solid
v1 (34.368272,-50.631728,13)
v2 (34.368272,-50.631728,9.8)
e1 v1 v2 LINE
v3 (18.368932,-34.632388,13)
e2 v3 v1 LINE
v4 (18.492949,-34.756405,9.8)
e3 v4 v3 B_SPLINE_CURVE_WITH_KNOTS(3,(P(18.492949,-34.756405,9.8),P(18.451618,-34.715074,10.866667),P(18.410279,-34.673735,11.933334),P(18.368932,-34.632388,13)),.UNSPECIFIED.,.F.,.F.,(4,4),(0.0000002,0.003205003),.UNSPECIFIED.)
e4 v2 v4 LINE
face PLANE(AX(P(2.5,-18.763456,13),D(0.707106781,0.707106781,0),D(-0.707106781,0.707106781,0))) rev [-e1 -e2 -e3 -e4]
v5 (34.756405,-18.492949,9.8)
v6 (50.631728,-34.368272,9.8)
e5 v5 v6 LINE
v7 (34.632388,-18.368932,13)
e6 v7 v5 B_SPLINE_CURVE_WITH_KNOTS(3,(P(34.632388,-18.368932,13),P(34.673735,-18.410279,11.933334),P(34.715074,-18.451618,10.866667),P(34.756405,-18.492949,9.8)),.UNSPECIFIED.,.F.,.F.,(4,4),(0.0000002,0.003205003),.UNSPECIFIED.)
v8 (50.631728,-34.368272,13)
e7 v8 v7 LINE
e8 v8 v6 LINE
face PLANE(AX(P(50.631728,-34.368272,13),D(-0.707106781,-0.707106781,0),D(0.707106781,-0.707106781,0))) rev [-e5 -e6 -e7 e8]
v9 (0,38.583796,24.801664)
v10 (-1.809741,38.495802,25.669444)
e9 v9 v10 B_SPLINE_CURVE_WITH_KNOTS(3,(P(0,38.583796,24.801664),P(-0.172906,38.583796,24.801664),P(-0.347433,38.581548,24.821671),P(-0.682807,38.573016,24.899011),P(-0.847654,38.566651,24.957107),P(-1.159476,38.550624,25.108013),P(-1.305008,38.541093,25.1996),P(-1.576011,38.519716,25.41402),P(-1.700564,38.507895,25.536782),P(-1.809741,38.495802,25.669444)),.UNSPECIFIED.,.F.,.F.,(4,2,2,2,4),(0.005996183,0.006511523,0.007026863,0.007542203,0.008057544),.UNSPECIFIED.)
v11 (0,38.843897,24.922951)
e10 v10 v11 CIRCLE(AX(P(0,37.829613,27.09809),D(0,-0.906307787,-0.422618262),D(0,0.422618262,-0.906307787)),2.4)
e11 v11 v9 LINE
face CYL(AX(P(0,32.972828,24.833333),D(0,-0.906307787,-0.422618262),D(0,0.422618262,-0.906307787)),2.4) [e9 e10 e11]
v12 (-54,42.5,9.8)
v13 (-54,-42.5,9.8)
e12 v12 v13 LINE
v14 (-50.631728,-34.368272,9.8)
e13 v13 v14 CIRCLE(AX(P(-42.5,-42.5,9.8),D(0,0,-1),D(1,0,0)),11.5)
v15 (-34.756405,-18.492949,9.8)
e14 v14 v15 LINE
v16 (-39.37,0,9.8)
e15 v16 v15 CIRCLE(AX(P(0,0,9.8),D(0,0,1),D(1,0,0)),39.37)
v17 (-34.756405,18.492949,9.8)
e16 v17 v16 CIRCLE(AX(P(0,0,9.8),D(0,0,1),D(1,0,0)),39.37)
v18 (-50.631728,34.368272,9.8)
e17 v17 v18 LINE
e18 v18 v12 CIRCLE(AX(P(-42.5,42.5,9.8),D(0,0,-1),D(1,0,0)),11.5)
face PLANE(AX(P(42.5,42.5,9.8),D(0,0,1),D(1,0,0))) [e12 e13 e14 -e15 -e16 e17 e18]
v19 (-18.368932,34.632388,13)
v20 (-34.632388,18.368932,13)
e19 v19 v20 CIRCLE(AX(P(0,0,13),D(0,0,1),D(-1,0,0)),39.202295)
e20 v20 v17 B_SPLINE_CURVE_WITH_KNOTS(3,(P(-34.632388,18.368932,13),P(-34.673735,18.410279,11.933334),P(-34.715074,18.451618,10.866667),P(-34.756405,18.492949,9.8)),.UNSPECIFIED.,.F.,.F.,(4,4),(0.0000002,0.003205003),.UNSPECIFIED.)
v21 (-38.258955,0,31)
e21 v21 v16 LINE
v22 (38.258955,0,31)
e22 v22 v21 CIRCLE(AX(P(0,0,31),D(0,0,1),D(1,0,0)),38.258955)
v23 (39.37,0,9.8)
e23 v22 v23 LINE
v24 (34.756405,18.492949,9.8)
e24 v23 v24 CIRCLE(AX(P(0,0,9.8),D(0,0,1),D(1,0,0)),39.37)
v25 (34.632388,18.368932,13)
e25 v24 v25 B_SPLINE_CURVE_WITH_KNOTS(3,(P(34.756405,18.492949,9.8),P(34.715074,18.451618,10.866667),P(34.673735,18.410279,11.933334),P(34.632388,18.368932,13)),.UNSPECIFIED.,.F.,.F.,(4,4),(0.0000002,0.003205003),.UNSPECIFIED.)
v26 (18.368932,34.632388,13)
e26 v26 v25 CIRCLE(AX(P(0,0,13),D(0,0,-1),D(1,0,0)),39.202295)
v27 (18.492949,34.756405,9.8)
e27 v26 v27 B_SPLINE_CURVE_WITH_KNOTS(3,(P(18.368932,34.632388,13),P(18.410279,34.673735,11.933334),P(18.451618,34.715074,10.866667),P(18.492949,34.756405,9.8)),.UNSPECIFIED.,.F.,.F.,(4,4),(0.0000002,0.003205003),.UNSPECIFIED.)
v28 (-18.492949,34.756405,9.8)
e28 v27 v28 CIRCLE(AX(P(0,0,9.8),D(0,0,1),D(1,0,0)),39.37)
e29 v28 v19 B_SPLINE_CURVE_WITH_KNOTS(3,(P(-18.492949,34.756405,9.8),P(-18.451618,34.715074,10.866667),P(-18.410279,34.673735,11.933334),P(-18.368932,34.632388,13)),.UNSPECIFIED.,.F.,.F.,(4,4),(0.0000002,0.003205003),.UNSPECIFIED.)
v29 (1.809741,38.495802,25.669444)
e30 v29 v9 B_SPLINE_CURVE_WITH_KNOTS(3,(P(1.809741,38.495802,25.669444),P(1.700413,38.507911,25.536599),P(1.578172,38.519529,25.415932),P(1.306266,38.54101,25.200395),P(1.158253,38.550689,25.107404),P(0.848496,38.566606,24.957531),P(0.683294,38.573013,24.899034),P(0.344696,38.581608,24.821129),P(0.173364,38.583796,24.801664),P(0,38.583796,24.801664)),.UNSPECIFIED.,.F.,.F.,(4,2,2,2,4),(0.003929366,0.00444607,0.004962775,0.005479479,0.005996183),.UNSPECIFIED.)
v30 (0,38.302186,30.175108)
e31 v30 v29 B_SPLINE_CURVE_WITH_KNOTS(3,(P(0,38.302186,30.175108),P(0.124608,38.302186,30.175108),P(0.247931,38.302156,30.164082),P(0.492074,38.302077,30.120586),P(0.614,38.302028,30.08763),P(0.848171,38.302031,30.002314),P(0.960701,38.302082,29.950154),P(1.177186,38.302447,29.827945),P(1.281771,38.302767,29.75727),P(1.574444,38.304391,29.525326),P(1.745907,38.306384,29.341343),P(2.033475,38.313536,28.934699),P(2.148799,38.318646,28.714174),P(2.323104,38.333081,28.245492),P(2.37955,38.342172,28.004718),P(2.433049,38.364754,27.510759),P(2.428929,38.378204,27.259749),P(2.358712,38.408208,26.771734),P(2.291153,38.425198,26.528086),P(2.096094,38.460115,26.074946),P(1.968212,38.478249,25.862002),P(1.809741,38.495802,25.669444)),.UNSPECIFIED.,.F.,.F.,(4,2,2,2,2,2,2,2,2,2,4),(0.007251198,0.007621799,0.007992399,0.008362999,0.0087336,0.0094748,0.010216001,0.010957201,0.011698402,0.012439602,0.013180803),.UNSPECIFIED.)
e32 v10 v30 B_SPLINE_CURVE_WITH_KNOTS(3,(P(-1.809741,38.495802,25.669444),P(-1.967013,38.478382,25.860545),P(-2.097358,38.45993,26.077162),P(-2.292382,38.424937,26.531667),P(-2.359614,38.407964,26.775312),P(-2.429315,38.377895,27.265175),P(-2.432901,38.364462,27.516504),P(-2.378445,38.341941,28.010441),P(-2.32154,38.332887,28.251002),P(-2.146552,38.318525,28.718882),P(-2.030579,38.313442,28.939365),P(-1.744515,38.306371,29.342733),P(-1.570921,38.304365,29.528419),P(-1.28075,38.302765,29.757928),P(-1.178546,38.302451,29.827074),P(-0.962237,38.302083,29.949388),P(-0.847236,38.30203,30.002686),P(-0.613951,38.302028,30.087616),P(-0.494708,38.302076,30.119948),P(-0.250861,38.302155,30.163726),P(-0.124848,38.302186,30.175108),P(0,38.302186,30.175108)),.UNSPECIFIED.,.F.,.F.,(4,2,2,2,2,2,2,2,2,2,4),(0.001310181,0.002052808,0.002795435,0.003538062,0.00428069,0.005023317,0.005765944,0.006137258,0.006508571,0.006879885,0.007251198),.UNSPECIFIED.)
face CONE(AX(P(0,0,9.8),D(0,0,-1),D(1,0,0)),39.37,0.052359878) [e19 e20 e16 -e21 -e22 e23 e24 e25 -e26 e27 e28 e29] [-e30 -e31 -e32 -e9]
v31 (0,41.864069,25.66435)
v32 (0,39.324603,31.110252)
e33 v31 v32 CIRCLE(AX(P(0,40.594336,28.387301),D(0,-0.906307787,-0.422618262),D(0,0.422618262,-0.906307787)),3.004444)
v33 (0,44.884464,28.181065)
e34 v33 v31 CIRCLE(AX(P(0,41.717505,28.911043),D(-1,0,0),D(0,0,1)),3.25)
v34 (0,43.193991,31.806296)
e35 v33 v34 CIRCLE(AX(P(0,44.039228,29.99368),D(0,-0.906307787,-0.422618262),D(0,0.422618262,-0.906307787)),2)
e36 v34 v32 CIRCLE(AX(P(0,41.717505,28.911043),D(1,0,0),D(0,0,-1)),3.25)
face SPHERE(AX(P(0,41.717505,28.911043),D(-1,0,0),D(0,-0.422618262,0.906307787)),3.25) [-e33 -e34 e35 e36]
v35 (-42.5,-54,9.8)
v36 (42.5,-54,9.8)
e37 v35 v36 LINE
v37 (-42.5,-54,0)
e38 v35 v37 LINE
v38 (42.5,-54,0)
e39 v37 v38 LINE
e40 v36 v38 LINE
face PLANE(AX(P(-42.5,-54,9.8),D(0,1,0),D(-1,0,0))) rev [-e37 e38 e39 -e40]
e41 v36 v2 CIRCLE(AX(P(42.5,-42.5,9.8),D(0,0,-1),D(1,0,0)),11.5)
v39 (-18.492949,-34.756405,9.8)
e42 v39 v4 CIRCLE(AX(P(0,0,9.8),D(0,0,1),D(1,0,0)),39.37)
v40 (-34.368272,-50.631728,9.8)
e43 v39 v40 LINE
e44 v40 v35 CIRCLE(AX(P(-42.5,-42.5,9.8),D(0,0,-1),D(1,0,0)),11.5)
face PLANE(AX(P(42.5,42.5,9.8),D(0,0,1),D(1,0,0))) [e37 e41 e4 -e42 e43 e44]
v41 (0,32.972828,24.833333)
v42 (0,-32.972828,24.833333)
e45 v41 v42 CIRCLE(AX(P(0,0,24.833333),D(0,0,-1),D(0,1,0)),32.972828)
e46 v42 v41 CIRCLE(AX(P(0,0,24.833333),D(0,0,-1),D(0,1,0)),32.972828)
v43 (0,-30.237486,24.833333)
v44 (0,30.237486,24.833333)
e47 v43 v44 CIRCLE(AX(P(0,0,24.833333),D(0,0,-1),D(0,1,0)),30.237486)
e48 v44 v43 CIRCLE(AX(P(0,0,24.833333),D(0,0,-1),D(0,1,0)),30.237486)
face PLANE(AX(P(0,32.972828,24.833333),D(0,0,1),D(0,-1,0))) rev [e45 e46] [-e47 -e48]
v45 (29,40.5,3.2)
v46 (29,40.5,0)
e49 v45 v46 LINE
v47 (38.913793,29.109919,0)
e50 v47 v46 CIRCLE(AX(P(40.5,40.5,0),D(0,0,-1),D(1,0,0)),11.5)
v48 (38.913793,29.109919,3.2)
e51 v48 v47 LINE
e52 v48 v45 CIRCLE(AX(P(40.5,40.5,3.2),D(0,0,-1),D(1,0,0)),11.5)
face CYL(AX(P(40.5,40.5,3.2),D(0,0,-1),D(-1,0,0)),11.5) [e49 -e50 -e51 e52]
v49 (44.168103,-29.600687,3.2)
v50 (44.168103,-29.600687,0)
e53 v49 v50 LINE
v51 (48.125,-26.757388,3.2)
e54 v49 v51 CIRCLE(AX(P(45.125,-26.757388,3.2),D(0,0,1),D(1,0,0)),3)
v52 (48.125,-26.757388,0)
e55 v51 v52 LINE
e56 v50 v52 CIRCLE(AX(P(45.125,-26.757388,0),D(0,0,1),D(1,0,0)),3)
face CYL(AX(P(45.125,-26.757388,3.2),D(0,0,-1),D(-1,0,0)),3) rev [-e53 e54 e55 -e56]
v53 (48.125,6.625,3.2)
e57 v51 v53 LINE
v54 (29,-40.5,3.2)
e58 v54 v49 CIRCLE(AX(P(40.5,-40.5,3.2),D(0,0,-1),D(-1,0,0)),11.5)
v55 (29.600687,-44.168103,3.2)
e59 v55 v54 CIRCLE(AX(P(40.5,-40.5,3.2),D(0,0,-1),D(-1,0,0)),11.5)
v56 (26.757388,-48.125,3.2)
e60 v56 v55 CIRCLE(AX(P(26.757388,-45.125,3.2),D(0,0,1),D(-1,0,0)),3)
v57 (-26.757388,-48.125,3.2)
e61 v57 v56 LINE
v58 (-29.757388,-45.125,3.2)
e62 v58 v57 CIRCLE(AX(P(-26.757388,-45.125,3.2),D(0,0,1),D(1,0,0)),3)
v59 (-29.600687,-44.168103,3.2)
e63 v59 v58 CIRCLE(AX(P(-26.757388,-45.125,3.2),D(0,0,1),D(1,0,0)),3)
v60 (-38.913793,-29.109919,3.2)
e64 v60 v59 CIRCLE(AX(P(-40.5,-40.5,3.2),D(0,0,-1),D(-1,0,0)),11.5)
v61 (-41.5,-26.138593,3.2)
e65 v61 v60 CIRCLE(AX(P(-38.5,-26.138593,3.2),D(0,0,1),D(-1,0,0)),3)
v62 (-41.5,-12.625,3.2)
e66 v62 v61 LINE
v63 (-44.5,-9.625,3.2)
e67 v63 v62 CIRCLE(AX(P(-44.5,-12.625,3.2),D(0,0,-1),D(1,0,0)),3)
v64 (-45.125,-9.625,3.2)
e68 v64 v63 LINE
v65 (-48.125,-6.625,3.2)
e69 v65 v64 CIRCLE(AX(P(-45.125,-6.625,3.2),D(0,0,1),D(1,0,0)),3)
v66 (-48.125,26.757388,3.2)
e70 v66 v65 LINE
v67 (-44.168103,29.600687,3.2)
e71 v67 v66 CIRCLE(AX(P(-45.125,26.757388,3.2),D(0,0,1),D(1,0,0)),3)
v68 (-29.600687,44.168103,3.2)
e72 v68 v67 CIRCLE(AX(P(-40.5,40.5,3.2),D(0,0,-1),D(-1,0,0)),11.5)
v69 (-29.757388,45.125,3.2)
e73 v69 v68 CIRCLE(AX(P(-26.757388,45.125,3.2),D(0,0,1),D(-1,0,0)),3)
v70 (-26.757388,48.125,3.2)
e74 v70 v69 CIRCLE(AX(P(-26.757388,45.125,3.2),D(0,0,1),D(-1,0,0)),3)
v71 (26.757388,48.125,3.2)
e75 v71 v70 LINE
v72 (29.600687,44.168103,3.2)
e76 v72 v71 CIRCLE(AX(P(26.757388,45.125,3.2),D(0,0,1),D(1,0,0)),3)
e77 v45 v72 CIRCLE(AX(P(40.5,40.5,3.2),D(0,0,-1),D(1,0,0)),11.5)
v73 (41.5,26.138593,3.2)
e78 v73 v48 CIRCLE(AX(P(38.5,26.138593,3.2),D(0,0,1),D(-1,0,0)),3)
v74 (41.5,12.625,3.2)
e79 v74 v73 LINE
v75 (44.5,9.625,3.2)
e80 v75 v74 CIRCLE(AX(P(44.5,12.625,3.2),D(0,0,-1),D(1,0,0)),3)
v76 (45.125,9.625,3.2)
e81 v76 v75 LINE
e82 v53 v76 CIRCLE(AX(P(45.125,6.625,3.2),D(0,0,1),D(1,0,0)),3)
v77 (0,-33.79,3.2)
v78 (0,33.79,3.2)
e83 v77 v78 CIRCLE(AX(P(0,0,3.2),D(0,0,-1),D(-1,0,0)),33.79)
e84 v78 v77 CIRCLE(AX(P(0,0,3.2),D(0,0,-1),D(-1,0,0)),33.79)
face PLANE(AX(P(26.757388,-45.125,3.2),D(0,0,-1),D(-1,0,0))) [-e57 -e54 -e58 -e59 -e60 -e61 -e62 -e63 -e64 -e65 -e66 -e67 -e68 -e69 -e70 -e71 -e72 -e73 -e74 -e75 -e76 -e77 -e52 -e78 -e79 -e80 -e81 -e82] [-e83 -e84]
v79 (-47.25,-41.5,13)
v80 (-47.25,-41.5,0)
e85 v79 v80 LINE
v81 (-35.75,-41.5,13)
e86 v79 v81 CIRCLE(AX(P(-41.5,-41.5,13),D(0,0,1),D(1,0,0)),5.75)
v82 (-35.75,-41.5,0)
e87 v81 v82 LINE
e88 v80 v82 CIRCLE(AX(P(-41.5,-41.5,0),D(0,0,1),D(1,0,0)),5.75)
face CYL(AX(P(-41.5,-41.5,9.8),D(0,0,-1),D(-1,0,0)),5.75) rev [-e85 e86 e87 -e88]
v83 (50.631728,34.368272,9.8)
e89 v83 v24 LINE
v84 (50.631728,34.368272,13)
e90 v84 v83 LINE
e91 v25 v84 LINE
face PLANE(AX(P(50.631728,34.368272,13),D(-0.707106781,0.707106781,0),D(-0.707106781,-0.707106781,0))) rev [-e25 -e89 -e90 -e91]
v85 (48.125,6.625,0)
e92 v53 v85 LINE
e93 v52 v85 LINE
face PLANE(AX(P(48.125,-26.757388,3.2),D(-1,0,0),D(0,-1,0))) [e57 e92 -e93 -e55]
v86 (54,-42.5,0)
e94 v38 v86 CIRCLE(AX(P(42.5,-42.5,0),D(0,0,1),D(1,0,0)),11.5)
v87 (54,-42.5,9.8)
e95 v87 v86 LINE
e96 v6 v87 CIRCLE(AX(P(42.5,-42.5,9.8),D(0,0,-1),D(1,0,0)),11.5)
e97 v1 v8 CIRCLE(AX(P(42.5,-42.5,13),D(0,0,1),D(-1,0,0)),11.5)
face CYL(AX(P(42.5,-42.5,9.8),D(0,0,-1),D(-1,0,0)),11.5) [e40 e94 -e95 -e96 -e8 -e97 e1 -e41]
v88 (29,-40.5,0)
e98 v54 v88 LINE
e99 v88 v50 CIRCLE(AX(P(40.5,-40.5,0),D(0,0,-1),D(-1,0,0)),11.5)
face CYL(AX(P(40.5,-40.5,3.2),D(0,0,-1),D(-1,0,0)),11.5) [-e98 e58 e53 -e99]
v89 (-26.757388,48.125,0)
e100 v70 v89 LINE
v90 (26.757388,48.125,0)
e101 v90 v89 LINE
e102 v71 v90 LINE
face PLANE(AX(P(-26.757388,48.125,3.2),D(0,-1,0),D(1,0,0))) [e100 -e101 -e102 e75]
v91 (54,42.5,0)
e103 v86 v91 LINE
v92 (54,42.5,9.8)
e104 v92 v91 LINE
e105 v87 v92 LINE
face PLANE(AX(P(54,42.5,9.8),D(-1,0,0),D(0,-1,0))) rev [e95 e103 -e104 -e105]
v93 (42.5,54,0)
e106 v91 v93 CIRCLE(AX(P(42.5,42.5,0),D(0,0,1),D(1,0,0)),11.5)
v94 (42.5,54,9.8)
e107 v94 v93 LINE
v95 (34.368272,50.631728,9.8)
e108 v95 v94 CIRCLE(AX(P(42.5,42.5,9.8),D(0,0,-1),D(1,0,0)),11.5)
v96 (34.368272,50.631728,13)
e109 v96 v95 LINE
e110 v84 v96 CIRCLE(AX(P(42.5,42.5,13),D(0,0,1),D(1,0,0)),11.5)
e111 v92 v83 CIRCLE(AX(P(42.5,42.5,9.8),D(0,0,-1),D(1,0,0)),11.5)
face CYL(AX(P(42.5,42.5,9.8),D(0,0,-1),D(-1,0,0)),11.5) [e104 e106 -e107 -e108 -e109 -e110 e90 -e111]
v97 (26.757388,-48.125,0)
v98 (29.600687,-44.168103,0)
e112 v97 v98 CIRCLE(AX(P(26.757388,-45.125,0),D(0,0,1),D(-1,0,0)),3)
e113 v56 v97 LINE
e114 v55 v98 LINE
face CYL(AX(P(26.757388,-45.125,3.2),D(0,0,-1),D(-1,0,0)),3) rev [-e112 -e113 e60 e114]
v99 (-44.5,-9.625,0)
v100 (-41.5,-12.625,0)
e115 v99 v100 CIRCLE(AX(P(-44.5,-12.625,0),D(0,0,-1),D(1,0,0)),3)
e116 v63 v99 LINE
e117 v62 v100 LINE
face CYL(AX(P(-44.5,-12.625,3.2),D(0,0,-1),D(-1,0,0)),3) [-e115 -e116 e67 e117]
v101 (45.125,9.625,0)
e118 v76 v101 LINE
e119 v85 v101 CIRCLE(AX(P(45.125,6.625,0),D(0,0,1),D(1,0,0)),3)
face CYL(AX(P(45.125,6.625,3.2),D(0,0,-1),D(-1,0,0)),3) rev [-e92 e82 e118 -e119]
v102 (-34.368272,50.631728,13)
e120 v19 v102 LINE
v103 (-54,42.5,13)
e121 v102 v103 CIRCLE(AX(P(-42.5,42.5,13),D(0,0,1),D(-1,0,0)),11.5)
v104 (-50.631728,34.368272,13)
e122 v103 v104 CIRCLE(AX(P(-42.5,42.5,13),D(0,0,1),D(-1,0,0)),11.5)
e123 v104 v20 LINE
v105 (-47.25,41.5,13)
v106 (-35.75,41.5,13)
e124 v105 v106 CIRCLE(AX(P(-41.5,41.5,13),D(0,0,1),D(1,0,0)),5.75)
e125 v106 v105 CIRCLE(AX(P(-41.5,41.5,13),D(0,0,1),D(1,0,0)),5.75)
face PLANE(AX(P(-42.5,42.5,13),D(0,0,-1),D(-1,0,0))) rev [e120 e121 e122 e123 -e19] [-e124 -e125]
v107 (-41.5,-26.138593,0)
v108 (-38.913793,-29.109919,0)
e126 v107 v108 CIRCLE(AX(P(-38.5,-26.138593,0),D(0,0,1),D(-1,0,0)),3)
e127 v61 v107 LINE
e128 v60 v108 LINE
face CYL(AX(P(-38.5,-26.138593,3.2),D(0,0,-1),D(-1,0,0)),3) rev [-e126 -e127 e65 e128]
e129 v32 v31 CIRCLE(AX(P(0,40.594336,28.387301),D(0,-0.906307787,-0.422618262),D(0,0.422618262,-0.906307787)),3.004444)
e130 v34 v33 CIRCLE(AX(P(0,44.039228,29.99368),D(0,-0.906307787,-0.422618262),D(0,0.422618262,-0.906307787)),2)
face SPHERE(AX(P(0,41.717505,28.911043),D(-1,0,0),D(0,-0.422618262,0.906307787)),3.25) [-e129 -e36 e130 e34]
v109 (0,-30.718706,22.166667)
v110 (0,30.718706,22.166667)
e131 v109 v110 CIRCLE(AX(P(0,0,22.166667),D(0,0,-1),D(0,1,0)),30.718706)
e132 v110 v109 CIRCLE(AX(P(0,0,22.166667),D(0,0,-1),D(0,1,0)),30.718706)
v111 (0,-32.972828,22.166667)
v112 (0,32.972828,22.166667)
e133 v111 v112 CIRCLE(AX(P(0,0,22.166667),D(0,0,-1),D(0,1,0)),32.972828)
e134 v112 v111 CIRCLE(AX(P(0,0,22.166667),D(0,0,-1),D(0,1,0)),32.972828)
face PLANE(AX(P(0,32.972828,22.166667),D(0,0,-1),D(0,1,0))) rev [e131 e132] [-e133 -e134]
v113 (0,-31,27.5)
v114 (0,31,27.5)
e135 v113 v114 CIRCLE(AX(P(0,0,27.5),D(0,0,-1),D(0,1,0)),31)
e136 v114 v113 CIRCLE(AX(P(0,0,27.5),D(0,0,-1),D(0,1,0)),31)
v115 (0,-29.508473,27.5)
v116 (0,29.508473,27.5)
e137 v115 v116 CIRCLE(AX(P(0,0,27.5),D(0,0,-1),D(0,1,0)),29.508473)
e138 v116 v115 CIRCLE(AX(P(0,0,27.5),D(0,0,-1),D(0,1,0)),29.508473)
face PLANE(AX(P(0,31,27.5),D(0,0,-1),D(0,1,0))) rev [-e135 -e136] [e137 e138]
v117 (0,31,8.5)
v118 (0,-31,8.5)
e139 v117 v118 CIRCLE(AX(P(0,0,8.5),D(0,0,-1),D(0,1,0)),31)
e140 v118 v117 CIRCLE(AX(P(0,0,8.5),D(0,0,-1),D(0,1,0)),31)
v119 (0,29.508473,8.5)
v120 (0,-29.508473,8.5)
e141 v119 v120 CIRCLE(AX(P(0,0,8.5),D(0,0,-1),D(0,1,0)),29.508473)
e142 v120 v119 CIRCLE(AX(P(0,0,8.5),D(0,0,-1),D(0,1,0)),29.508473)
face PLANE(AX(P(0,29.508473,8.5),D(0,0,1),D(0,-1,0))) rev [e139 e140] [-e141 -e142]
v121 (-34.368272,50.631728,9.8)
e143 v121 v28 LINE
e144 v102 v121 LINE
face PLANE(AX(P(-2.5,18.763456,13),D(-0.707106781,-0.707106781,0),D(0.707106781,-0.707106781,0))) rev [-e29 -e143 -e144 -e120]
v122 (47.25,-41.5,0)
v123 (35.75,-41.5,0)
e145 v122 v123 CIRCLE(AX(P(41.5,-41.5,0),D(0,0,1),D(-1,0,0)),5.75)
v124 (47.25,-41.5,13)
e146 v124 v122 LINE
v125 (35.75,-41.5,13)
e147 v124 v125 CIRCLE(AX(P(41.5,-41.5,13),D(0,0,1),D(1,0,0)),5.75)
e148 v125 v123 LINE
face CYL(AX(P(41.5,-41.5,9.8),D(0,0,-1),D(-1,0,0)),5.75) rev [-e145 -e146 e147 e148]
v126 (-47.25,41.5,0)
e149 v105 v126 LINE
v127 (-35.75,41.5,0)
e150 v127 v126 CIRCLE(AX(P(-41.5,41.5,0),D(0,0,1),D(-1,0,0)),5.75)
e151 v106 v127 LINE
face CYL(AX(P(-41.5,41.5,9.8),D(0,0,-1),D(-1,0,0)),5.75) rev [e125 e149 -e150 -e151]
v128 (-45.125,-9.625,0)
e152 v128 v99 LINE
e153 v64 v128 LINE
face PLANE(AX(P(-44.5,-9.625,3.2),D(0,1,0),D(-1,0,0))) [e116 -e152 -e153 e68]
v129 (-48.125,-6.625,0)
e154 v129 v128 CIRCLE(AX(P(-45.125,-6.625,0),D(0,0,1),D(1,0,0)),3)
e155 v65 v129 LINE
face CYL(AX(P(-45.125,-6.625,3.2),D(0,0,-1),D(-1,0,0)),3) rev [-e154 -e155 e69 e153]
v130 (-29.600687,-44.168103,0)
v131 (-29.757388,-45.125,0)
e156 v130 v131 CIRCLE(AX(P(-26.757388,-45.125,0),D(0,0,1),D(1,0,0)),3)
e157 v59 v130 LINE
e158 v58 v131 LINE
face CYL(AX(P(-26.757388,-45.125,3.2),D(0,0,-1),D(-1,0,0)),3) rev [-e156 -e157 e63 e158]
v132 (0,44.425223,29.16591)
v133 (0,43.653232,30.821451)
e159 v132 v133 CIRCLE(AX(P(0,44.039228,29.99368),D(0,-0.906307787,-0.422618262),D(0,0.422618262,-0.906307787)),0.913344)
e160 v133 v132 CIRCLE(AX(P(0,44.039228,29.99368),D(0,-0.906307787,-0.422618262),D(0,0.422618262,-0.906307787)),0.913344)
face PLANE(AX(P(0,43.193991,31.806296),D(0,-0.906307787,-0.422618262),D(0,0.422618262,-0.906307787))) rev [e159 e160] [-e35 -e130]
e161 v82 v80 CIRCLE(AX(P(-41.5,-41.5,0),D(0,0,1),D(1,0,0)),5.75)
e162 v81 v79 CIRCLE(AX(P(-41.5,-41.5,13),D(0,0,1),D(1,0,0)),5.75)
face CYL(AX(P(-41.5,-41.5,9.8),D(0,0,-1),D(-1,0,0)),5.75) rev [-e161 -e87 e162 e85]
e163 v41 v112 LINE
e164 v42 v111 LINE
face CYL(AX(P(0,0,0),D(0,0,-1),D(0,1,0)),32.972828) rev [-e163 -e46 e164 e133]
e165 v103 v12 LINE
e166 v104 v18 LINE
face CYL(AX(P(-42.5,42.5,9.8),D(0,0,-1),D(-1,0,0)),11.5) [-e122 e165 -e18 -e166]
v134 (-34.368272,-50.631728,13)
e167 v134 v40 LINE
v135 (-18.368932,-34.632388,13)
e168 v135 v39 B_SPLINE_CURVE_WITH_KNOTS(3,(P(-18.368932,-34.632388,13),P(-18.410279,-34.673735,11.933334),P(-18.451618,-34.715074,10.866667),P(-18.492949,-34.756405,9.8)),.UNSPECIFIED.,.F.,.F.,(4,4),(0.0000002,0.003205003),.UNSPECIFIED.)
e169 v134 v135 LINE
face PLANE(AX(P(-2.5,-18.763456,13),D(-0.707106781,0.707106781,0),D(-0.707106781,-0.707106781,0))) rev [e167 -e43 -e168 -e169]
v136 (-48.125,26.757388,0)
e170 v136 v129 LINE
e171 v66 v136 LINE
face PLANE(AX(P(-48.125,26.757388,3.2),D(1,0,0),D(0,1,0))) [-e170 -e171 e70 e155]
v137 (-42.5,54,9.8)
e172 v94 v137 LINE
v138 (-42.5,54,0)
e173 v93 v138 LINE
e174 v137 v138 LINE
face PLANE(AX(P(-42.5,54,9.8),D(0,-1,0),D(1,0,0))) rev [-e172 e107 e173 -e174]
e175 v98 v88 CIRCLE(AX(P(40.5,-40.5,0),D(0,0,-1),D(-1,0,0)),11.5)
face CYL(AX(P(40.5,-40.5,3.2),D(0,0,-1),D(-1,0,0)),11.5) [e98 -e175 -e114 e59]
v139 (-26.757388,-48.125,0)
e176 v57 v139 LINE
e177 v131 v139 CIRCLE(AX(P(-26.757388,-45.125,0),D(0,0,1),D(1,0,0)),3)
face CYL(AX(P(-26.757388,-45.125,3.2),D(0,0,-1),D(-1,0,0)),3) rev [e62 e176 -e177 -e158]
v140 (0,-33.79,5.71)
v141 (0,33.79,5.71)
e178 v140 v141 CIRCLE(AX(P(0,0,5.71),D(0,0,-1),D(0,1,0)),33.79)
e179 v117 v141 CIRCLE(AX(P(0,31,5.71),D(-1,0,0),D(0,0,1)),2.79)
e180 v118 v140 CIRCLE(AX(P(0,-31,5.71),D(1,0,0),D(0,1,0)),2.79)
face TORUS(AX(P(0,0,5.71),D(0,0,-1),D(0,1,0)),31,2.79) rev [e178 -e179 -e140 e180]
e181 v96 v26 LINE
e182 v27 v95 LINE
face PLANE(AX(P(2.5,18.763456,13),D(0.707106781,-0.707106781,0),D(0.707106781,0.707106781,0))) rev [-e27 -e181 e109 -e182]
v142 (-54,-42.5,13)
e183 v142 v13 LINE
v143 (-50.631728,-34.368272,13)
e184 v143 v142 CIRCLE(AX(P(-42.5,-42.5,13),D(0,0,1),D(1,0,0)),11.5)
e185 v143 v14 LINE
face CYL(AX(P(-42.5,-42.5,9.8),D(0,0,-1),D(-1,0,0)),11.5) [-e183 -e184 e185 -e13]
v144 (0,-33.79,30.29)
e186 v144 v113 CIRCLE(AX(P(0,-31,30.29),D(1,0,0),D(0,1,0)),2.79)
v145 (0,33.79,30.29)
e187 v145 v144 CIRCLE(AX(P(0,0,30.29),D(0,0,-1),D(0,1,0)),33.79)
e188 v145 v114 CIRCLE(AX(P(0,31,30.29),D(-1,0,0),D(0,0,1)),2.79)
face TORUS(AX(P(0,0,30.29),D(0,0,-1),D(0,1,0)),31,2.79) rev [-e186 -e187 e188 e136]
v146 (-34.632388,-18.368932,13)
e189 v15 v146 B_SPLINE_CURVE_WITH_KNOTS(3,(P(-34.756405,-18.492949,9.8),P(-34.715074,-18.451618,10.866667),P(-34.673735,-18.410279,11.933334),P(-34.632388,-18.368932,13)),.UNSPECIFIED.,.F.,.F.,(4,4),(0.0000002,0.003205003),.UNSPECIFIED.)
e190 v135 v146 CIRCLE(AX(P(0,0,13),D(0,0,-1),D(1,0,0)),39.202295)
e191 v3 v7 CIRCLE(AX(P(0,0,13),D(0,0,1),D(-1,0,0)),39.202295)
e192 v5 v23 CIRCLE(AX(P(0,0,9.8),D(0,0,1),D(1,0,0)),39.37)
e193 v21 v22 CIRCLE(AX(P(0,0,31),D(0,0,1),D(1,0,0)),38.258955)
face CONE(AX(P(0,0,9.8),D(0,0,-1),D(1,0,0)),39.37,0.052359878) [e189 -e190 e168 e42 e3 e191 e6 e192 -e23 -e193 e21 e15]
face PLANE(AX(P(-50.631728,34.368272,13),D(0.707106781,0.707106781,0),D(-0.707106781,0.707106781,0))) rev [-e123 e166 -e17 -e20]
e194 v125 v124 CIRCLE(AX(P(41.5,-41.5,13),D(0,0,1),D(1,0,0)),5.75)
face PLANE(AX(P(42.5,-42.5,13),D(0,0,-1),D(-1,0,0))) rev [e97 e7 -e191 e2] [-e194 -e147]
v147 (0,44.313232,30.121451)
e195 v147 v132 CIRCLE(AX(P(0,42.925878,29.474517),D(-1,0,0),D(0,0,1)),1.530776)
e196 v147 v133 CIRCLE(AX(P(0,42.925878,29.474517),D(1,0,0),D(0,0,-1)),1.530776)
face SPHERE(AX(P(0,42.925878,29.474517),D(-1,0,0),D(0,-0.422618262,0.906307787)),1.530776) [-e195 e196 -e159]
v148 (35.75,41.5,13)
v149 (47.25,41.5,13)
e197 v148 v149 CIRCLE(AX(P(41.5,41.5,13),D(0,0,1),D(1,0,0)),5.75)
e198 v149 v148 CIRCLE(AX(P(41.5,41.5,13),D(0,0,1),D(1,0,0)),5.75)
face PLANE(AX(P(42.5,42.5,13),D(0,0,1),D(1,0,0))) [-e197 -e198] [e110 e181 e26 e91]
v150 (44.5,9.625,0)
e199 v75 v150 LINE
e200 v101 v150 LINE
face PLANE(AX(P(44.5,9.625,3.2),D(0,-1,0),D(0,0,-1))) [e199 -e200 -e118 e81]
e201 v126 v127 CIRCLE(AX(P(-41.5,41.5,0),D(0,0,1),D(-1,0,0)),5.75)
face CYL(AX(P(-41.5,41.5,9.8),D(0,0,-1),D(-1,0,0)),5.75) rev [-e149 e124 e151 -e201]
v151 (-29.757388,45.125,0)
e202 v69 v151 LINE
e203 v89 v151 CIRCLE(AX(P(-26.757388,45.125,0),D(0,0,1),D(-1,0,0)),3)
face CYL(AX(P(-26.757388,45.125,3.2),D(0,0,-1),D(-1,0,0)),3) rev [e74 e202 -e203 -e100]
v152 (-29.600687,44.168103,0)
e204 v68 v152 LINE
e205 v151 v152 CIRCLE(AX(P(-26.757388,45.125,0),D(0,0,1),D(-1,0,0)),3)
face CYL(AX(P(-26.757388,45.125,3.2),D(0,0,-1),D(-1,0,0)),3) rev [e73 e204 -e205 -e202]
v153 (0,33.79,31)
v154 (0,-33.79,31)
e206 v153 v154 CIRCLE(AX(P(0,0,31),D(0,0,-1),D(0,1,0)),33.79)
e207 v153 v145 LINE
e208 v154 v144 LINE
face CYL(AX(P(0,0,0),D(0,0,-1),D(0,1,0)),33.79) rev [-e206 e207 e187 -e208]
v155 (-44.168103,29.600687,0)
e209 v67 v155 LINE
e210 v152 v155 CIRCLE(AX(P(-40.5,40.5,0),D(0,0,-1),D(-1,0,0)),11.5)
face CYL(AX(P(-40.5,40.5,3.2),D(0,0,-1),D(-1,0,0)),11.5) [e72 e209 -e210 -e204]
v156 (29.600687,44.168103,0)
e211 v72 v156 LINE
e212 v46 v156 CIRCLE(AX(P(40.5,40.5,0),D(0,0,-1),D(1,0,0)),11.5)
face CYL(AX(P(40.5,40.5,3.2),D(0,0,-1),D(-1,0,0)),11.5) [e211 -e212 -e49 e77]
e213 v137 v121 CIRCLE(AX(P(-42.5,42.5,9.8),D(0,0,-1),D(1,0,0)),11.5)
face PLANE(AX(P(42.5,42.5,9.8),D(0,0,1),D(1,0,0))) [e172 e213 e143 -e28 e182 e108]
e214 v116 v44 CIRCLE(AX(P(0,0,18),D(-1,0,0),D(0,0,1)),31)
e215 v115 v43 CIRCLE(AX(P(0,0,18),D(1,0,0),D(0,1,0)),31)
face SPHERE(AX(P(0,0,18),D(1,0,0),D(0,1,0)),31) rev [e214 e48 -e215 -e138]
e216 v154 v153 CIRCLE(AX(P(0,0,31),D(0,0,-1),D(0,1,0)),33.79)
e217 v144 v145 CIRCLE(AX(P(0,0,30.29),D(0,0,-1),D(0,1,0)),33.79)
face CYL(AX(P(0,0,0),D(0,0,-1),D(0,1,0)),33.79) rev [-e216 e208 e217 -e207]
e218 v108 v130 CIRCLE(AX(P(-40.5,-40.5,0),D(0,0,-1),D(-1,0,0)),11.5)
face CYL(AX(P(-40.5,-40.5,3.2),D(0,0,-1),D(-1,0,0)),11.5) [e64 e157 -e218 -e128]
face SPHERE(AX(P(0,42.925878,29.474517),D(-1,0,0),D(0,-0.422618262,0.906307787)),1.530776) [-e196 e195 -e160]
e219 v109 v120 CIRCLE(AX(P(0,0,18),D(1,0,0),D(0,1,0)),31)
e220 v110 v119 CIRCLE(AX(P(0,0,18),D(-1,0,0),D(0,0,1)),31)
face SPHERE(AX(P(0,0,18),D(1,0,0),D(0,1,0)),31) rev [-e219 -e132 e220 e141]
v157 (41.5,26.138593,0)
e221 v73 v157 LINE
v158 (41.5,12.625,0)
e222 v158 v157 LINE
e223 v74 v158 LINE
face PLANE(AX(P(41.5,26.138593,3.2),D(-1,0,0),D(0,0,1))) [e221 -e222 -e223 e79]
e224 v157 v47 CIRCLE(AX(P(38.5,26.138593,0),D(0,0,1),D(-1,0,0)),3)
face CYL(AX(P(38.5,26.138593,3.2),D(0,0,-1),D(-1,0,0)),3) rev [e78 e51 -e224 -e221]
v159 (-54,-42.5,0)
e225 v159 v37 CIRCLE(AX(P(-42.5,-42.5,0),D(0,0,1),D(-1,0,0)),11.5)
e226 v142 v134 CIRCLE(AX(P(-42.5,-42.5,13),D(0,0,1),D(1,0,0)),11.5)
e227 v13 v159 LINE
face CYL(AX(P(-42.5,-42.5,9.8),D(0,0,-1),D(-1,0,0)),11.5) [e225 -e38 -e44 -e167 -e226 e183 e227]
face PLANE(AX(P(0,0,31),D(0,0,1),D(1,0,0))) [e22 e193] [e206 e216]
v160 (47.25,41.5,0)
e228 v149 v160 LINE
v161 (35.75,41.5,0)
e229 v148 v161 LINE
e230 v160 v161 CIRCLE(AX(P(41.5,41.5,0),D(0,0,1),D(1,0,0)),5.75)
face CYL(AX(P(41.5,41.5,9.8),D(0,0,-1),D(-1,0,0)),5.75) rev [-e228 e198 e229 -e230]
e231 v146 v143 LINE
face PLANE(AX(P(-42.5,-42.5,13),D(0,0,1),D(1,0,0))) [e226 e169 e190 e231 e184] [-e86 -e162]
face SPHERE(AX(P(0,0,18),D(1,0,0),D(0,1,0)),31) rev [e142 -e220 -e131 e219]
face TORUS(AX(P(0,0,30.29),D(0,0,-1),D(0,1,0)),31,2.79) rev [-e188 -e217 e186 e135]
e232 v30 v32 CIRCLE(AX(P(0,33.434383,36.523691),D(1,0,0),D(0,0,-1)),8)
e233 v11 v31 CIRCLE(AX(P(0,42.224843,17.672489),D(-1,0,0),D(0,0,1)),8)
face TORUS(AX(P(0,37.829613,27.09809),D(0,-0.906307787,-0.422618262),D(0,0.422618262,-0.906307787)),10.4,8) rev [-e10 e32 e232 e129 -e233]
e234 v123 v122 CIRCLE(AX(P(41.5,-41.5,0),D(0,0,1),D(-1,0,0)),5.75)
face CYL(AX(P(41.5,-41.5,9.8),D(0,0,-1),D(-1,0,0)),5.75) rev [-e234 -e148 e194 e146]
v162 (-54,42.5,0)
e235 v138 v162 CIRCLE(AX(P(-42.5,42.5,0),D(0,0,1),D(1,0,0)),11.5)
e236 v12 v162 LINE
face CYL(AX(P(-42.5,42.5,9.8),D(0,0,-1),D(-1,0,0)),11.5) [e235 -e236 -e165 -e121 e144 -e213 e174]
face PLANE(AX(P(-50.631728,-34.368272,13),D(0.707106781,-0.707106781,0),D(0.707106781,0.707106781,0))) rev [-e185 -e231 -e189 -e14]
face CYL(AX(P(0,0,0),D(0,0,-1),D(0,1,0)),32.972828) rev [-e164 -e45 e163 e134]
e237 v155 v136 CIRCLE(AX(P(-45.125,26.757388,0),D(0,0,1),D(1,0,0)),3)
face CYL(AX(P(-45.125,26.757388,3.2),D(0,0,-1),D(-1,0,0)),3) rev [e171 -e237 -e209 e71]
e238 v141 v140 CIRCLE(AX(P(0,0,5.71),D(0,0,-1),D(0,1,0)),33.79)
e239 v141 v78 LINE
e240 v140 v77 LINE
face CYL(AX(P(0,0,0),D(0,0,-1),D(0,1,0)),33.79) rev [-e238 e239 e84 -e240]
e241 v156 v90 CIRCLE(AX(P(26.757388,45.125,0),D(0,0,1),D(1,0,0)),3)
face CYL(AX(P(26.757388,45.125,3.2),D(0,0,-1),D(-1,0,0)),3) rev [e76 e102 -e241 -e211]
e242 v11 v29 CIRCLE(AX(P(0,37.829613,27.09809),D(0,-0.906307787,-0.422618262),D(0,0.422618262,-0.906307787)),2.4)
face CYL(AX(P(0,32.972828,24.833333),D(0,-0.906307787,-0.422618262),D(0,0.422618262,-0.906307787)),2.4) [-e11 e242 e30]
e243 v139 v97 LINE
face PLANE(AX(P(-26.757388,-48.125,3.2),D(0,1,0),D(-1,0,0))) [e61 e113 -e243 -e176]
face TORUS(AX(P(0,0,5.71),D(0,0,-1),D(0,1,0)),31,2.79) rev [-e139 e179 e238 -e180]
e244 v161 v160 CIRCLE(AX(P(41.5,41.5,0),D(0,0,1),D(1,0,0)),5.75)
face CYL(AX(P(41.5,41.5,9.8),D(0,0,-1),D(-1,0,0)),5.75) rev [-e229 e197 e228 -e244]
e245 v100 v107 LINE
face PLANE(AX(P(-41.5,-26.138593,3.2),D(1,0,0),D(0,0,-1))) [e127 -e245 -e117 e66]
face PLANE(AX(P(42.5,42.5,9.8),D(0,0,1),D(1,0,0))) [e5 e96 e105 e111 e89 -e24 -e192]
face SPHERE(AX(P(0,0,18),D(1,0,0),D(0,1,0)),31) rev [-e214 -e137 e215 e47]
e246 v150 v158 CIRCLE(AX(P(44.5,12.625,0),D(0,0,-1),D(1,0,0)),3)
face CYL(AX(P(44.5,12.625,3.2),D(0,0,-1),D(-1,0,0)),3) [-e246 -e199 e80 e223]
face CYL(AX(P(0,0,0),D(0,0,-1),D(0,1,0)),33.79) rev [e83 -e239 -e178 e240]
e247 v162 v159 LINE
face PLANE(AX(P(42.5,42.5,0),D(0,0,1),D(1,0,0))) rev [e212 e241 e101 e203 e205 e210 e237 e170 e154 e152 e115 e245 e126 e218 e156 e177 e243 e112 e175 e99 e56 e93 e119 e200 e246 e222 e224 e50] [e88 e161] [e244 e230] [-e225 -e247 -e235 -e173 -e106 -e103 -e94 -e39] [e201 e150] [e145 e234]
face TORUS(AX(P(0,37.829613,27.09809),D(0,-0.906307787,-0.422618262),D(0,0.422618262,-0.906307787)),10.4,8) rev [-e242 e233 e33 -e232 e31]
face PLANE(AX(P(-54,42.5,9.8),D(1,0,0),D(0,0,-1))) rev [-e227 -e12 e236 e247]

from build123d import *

# Parameters (mm, degrees)
SKETCH_1_R          = 5.75
EXTRUDE_686_DEPTH   = 9.8
SKETCH_2_R          = 5.75
EXTRUDE_1_DEPTH     = 13
CUT_EXTRUDE_3_DEPTH = 3.2
SKETCH_4_R          = 39.37
EXTRUDE_2_DEPTH     = 21.2
EXTRUDE_2_TAPER     = 3


with BuildPart() as part:
    # 草图1 → Extrude 686 (new body)
    with BuildSketch(Plane.XY):
        with BuildLine():
            Line((-42.5, -54), (42.5, -54))
            ThreePointArc((42.5, -54), (50.631727984, -50.631727984), (54, -42.5))
            Line((54, -42.5), (54, 42.5))
            ThreePointArc((54, 42.5), (50.631727984, 50.631727984), (42.5, 54))
            Line((42.5, 54), (-42.5, 54))
            ThreePointArc((-42.5, 54), (-50.631727984, 50.631727984), (-54, 42.5))
            Line((-54, 42.5), (-54, -42.5))
            ThreePointArc((-54, -42.5), (-50.631727984, -50.631727984), (-42.5, -54))
        make_face()
        with Locations((-41.5, -41.5)):
            Circle(SKETCH_1_R, mode=Mode.SUBTRACT)
        with Locations(Location((-41.5, 41.5, 0), (0, 0, 180))):
            Circle(SKETCH_1_R, mode=Mode.SUBTRACT)
        with Locations(Location((41.5, -41.5, 0), (0, 0, 180))):
            Circle(SKETCH_1_R, mode=Mode.SUBTRACT)
        with Locations((41.5, 41.5)):
            Circle(SKETCH_1_R, mode=Mode.SUBTRACT)
    extrude(amount=EXTRUDE_686_DEPTH)

    # 草图2 → 凸台-拉伸1 (add)
    # profile 1 of 4: a face of its own
    with BuildSketch(Plane.XY):
        with BuildLine():
            Line((-50.631727984, -34.368272016), (-18.763455967, -2.5))
            Line((-18.763455967, -2.5), (-2.5, -18.763455967))
            Line((-2.5, -18.763455967), (-34.368272016, -50.631727984))
            ThreePointArc((-34.368272016, -50.631727984), (-50.631727984, -50.631727984), (-50.631727984, -34.368272016))
        make_face()
        with Locations((-41.5, -41.5)):
            Circle(SKETCH_2_R, mode=Mode.SUBTRACT)
    # profile 2 of 4: a face of its own
    with BuildSketch(Plane.XY):
        with BuildLine():
            Line((-18.763455967, 2.5), (-2.5, 18.763455967))
            Line((-2.5, 18.763455967), (-34.368272016, 50.631727984))
            ThreePointArc((-34.368272016, 50.631727984), (-50.631727984, 50.631727984), (-50.631727984, 34.368272016))
            Line((-50.631727984, 34.368272016), (-18.763455967, 2.5))
        make_face()
        with Locations(Location((-41.5, 41.5, 0), (0, 0, 180))):
            Circle(SKETCH_2_R, mode=Mode.SUBTRACT)
    # profile 3 of 4: a face of its own
    with BuildSketch(Plane.XY):
        with BuildLine():
            Line((2.5, -18.763455967), (34.368272016, -50.631727984))
            ThreePointArc((34.368272016, -50.631727984), (50.631727984, -50.631727984), (50.631727984, -34.368272016))
            Line((50.631727984, -34.368272016), (18.763455967, -2.5))
            Line((18.763455967, -2.5), (2.5, -18.763455967))
        make_face()
        with Locations(Location((41.5, -41.5, 0), (0, 0, 180))):
            Circle(SKETCH_2_R, mode=Mode.SUBTRACT)
    # profile 4 of 4: a face of its own
    with BuildSketch(Plane.XY):
        with BuildLine():
            Line((2.5, 18.763455967), (34.368272016, 50.631727984))
            ThreePointArc((34.368272016, 50.631727984), (50.631727984, 50.631727984), (50.631727984, 34.368272016))
            Line((50.631727984, 34.368272016), (18.763455967, 2.5))
            Line((18.763455967, 2.5), (2.5, 18.763455967))
        make_face()
        with Locations((41.5, 41.5)):
            Circle(SKETCH_2_R, mode=Mode.SUBTRACT)
    extrude(amount=EXTRUDE_1_DEPTH)

    # 草图3 → 切除-拉伸3 (cut)
    with BuildSketch(Plane.XY):
        with BuildLine():
            Line((-26.757388349, 48.125), (26.757388349, 48.125))
            ThreePointArc((26.757388349, 48.125), (29.193644663, 46.875615655), (29.600687311, 44.168103448))
            ThreePointArc((29.600687311, 44.168103448), (30.719443759, 34.450973663), (38.913793103, 29.10991889))
            ThreePointArc((38.913793103, 29.10991889), (40.762894088, 28.108189877), (41.5, 26.138593384))
            Line((41.5, 26.138593384), (41.5, 12.625))
            ThreePointArc((41.5, 12.625), (42.378679656, 10.503679656), (44.5, 9.625))
            Line((44.5, 9.625), (45.125, 9.625))
            ThreePointArc((45.125, 9.625), (47.246320344, 8.746320344), (48.125, 6.625))
            Line((48.125, 6.625), (48.125, -26.757388349))
            ThreePointArc((48.125, -26.757388349), (46.875615655, -29.193644663), (44.168103448, -29.600687311))
            ThreePointArc((44.168103448, -29.600687311), (32.368272016, -32.368272016), (29.600687311, -44.168103448))
            ThreePointArc((29.600687311, -44.168103448), (29.193644663, -46.875615655), (26.757388349, -48.125))
            Line((26.757388349, -48.125), (-26.757388349, -48.125))
            ThreePointArc((-26.757388349, -48.125), (-29.193644663, -46.875615655), (-29.600687311, -44.168103448))
            ThreePointArc((-29.600687311, -44.168103448), (-30.719443759, -34.450973663), (-38.913793103, -29.10991889))
            ThreePointArc((-38.913793103, -29.10991889), (-40.762894088, -28.108189877), (-41.5, -26.138593384))
            Line((-41.5, -26.138593384), (-41.5, -12.625))
            ThreePointArc((-41.5, -12.625), (-42.378679656, -10.503679656), (-44.5, -9.625))
            Line((-44.5, -9.625), (-45.125, -9.625))
            ThreePointArc((-45.125, -9.625), (-47.246320344, -8.746320344), (-48.125, -6.625))
            Line((-48.125, -6.625), (-48.125, 26.757388349))
            ThreePointArc((-48.125, 26.757388349), (-46.875615655, 29.193644663), (-44.168103448, 29.600687311))
            ThreePointArc((-44.168103448, 29.600687311), (-32.368272016, 32.368272016), (-29.600687311, 44.168103448))
            ThreePointArc((-29.600687311, 44.168103448), (-29.193644663, 46.875615655), (-26.757388349, 48.125))
        make_face()
    extrude(amount=CUT_EXTRUDE_3_DEPTH, mode=Mode.SUBTRACT)

    # 草图4 → 凸台-拉伸2 (add)
    with BuildSketch(Plane.XY.offset(9.8)):
        Circle(SKETCH_4_R)
    extrude(amount=EXTRUDE_2_DEPTH, taper=EXTRUDE_2_TAPER)

    # 草图5 → 切除-旋转1 (revolve, cut)
    with BuildSketch(Plane(origin=(0, 0, 0), x_dir=(0, 0, -1), z_dir=(1, 0, 0))):
        with BuildLine():
            Line((-31, 33.79), (-30.29, 33.79))
            ThreePointArc((-30.29, 33.79), (-28.31717208, 32.97282792), (-27.5, 31))
            Line((-27.5, 31), (-27.5, 29.508473359))
            ThreePointArc((-27.5, 29.508473359), (-26.174797201, 29.902720457), (-24.833333333, 30.237485933))
            Line((-24.833333333, 30.237485933), (-24.833333333, 32.97282792))
            Line((-24.833333333, 32.97282792), (-22.166666667, 32.97282792))
            Line((-22.166666667, 32.97282792), (-22.166666667, 30.718705847))
            ThreePointArc((-22.166666667, 30.718705847), (-15.265539033, 30.879163253), (-8.5, 29.508473359))
            Line((-8.5, 29.508473359), (-8.5, 31))
            ThreePointArc((-8.5, 31), (-7.68282792, 32.97282792), (-5.71, 33.79))
            Line((-5.71, 33.79), (0, 33.79))
            Line((0, 33.79), (0, 0))
            Line((0, 0), (-31, 0))
            Line((-31, 0), (-31, 33.79))
        make_face()
    revolve(axis=Axis((0, 0, 0), (0, 0, 1)), mode=Mode.SUBTRACT)

    # 草图6 → 凸台-旋转1 (revolve)
    with BuildSketch(Plane(origin=(0, 0, 0), x_dir=(0, 0, -1), z_dir=(1, 0, 0))):
        with BuildLine():
            Line((-28.142278533, 34.39), (-25.967139844, 35.404283828))
            Line((-25.967139844, 35.404283828), (-30.121450593, 44.313231979))
            ThreePointArc((-30.121450593, 44.313231979), (-30.524648689, 44.039654202), (-30.821450593, 43.653231979))
            Line((-30.821450593, 43.653231979), (-31.806295837, 43.193991099))
            ThreePointArc((-31.806295837, 43.193991099), (-32.109703255, 41.142115004), (-31.110252397, 39.324603091))
            ThreePointArc((-31.110252397, 39.324603091), (-30.068637739, 38.160089016), (-29.27322829, 36.815329582))
            Line((-29.27322829, 36.815329582), (-28.142278533, 34.39))
        make_face()
    revolve(axis=Axis((0, 32.97282792, 24.833333333), (0, 0.9063077870366524, 0.42261826174069445)))


solid = part.part
